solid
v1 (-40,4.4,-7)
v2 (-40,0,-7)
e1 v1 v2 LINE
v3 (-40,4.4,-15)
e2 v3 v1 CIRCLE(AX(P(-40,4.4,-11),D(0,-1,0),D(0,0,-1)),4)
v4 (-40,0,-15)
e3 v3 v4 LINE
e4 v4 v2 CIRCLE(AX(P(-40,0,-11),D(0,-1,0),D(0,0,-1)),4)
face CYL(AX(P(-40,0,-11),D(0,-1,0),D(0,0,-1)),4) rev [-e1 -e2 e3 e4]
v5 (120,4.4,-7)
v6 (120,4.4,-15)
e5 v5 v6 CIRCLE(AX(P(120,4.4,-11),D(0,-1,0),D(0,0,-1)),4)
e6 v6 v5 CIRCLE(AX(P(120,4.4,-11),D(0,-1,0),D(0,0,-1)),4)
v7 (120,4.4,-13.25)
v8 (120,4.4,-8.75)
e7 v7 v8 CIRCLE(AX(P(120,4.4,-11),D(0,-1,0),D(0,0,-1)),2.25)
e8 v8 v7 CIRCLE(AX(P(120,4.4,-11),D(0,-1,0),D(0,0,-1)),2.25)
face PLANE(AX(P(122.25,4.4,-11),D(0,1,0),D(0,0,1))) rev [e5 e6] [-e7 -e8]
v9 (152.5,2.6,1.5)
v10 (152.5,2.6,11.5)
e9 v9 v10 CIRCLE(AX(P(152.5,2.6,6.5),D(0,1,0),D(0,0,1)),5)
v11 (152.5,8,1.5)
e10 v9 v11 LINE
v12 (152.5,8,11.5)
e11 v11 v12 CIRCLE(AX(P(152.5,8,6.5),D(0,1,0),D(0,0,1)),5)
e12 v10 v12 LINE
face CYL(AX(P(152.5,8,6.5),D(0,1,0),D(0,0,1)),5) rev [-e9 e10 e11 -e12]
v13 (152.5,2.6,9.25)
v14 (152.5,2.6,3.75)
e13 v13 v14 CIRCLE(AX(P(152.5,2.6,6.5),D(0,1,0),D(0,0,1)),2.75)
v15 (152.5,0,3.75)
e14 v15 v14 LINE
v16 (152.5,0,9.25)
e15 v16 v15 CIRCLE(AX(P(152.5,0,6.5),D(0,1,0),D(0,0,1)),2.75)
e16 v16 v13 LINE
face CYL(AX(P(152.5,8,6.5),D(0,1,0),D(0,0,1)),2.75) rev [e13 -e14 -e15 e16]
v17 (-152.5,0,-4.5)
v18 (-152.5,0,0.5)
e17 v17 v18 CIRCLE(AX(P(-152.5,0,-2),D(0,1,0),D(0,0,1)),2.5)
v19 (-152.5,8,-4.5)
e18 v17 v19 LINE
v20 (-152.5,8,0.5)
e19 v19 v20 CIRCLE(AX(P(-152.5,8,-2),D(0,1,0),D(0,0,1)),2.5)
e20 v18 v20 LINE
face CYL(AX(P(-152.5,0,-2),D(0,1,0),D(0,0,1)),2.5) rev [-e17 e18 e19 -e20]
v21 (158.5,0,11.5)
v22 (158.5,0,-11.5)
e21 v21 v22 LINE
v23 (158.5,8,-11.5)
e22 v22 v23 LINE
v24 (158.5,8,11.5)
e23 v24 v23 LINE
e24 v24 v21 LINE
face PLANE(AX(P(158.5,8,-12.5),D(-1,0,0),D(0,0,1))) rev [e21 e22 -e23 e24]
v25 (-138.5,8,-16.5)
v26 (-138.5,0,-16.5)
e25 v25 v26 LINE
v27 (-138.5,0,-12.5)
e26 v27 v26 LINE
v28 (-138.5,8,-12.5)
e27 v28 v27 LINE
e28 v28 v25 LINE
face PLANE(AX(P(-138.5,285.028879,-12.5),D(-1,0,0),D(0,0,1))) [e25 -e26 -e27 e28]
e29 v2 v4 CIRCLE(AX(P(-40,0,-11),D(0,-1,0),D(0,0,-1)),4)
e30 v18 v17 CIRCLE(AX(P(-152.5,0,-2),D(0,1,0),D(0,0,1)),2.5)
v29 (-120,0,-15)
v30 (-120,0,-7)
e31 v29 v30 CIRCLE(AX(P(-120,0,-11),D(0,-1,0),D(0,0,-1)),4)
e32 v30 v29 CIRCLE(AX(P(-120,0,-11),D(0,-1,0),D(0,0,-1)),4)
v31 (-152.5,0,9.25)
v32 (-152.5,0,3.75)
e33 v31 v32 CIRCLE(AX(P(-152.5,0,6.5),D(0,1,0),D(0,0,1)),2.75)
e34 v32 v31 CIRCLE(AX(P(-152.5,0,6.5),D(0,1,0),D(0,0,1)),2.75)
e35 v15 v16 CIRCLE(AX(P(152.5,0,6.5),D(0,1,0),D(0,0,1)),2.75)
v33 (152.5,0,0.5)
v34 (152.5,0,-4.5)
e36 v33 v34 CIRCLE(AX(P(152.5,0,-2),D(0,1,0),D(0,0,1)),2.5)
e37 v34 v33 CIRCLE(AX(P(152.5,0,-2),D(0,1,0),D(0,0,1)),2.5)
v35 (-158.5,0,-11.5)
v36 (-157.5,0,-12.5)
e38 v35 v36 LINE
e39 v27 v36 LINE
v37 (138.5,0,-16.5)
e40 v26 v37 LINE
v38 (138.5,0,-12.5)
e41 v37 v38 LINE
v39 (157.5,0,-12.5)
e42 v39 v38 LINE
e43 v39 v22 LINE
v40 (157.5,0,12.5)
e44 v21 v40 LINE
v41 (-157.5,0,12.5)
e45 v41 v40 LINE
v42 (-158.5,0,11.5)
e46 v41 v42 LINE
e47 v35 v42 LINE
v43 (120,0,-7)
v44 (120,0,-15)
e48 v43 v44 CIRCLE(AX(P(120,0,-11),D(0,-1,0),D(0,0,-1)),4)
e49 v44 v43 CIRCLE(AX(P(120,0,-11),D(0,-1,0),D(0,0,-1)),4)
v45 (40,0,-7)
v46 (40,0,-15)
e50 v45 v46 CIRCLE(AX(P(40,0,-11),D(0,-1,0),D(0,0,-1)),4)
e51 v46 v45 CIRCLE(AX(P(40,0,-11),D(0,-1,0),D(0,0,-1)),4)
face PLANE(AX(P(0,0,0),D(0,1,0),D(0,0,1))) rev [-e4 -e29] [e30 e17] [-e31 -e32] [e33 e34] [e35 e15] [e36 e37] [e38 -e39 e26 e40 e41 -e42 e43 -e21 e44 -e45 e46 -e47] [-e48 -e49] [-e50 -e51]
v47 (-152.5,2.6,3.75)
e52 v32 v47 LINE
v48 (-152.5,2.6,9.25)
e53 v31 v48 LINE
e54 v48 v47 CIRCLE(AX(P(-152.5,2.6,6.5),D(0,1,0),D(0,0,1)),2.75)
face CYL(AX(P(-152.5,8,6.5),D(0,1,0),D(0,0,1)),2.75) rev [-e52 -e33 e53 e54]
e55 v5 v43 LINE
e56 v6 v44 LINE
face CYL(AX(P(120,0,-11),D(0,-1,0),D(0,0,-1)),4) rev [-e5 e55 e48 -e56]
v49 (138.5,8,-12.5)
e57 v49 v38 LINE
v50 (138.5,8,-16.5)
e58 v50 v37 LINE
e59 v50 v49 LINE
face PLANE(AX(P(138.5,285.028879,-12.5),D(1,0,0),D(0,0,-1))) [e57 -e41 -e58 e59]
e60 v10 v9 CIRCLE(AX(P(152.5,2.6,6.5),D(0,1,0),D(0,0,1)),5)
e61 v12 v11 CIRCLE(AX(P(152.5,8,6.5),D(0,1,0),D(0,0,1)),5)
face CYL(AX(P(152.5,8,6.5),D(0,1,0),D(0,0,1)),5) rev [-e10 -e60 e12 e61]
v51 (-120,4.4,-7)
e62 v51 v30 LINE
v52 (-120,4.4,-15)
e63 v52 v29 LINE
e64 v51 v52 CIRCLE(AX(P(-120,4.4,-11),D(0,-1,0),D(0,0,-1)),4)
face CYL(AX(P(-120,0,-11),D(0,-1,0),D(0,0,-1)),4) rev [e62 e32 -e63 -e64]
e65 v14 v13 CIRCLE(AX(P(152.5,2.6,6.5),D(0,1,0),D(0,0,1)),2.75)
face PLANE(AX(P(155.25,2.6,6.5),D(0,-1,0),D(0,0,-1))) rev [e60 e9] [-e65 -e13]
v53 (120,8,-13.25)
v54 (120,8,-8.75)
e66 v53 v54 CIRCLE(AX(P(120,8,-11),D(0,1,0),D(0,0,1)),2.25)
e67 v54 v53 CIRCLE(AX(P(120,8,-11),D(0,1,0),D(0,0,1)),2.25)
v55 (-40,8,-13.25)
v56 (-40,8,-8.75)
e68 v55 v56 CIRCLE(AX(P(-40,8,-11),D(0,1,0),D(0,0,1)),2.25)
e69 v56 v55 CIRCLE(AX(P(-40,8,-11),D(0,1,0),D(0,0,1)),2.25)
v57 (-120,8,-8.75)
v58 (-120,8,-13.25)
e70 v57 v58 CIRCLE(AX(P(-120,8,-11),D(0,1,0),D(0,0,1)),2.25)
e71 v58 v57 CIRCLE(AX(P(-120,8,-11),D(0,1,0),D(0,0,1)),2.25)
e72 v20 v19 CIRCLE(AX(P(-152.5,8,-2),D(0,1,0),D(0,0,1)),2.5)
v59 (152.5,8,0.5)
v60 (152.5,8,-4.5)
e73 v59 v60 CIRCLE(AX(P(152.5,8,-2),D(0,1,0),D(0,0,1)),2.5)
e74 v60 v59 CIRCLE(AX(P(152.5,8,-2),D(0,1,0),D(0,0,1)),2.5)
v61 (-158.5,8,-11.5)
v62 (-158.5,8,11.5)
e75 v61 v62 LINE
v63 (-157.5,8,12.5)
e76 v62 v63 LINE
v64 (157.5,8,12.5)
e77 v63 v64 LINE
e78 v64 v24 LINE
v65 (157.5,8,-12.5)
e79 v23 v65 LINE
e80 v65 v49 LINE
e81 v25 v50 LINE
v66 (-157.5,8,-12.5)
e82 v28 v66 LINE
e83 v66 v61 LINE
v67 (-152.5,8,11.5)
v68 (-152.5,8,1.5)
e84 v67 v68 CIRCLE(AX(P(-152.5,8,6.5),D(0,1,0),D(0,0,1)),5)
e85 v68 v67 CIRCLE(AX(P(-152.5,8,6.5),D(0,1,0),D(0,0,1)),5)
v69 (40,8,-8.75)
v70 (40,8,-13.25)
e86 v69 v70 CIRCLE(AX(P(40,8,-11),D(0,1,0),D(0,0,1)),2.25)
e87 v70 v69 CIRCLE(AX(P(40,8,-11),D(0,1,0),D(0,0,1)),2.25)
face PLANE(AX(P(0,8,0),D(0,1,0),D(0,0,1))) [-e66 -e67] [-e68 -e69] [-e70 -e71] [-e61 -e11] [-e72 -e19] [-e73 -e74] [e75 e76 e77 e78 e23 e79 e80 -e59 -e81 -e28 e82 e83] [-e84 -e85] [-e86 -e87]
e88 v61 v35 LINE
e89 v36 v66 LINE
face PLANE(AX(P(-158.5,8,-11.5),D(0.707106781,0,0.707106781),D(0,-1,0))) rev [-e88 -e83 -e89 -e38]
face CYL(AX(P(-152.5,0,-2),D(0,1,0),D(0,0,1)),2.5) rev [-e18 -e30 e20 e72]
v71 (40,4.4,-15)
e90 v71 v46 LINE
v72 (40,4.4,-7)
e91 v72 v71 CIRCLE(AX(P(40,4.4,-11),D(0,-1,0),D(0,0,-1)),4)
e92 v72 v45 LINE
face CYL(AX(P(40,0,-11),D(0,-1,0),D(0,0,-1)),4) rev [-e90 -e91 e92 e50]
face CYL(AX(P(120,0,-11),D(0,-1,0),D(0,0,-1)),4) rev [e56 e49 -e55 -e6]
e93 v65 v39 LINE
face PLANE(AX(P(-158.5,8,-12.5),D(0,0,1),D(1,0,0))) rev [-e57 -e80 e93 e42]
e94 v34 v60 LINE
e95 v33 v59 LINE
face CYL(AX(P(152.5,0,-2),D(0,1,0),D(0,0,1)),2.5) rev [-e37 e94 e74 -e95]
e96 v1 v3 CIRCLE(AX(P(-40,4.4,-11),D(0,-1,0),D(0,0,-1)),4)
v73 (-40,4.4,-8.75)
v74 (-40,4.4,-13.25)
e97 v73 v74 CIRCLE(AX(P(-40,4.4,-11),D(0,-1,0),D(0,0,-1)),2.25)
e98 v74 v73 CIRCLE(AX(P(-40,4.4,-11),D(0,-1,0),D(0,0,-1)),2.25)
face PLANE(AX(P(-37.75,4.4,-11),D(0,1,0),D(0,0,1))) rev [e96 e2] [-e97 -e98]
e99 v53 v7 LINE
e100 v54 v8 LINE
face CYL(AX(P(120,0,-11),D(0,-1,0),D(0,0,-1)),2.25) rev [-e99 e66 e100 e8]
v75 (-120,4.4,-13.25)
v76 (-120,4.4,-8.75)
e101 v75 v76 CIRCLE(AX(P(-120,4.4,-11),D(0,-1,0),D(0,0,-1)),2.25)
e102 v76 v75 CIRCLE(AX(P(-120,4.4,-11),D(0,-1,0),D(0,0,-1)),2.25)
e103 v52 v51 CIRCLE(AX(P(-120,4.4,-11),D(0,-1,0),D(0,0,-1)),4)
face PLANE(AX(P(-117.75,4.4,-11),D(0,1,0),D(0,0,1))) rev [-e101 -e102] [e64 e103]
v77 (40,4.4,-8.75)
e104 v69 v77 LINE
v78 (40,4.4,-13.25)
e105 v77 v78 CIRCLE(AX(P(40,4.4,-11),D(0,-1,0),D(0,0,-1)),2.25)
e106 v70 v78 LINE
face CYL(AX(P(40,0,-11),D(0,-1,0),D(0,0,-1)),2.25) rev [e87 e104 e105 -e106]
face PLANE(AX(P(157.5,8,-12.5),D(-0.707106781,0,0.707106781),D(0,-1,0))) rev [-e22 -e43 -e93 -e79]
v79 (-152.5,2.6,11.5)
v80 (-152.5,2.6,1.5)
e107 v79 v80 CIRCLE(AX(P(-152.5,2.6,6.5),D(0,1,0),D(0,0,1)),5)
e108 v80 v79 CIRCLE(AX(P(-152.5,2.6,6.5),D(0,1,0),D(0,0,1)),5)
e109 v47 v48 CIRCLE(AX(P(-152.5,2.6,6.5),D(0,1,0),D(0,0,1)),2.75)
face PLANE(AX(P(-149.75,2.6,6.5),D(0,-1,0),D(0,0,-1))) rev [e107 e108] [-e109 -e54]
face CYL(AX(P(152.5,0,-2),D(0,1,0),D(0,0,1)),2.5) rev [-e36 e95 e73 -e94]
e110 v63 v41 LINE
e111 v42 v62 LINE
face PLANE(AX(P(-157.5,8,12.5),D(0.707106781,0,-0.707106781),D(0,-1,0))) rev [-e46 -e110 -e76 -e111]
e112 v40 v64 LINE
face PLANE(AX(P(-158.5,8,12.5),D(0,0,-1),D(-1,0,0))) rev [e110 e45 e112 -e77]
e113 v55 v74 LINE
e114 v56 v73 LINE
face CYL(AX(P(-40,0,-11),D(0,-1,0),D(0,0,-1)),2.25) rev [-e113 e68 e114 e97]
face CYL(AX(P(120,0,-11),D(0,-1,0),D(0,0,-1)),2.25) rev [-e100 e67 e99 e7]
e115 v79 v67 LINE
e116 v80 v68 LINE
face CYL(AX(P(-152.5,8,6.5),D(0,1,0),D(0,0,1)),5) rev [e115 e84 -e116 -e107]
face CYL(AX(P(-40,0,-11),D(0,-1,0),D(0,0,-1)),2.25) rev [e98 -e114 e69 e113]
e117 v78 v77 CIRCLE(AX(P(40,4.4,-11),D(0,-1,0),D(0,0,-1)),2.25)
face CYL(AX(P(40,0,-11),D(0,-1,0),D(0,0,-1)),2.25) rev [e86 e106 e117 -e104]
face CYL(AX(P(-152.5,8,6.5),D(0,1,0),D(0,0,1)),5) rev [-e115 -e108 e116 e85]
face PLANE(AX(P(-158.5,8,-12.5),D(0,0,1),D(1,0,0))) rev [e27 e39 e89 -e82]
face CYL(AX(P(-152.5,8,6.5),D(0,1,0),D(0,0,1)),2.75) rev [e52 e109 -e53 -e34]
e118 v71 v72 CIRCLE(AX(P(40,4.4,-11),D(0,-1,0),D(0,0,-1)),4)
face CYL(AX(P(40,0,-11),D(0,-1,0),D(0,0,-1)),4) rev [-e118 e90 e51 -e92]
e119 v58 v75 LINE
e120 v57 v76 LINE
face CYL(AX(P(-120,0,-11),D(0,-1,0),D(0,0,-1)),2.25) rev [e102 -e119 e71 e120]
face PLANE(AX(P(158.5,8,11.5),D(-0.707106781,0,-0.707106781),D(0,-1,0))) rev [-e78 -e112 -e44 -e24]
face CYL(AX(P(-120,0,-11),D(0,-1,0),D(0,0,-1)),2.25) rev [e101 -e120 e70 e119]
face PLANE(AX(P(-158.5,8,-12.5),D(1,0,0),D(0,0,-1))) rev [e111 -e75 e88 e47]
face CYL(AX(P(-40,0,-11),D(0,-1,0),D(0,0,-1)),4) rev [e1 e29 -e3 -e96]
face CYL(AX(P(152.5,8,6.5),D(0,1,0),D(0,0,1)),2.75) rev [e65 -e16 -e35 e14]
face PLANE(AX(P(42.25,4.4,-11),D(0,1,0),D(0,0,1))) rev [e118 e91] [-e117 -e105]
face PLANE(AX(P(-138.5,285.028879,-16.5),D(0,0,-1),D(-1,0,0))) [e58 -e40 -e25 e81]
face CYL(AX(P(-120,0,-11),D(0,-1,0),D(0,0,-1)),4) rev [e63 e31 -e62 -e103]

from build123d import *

# Parameters (mm, degrees)
SKETCH_1_W                   = 317
SKETCH_1_H                   = 25
EXTRUDE_1_DEPTH              = 8
HOLE_WIZARD_M5_1_D           = 5.5
HOLE_WIZARD_M5_1_CBORE_D     = 10
HOLE_WIZARD_M5_1_CBORE_DEPTH = 5.4
SKETCH_4_R                   = 2.5
CUT_EXTRUDE_1_DEPTH          = 160.193278753
SKETCH_7_W                   = 277
SKETCH_7_H                   = 4
EXTRUDE_2_DEPTH              = 8
HOLE_WIZARD_M4_1_D           = 4.5
HOLE_WIZARD_M4_1_CBORE_D     = 8
HOLE_WIZARD_M4_1_CBORE_DEPTH = 4.4
CHAMFER_3_SIZE               = 1


with BuildPart() as part:
    # 草图1 → 凸台-拉伸1 (new body)
    with BuildSketch(Plane(origin=(0, 0, 0), x_dir=(1, 0, 0), z_dir=(0, 1, 0))):
        Rectangle(SKETCH_1_W, SKETCH_1_H)
    extrude(amount=EXTRUDE_1_DEPTH)

    # M5 六角凹头螺钉的柱形沉头孔1 (through all)
    with Locations(Plane(origin=(0, 8, 0), x_dir=(1, 0, 0), z_dir=(0, 1, 0))):
        with Locations((-152.5, -6.5), (152.5, -6.5)):
            CounterBoreHole(HOLE_WIZARD_M5_1_D / 2, HOLE_WIZARD_M5_1_CBORE_D / 2, HOLE_WIZARD_M5_1_CBORE_DEPTH)

    # 草图4 → 切除-拉伸1 (cut, through all)
    with BuildSketch(Plane(origin=(0, 8, 0), x_dir=(1, 0, 0), z_dir=(0, 1, 0))):
        with Locations(Location((-152.5, 2, 0), (0, 0, 270))):
            Circle(SKETCH_4_R)
        with Locations(Location((152.5, 2, 0), (0, 0, 270))):
            Circle(SKETCH_4_R)
    extrude(amount=-CUT_EXTRUDE_1_DEPTH, mode=Mode.SUBTRACT)

    # 草图7 → 凸台-拉伸2 (add)
    with BuildSketch(Plane.XZ):
        with Locations((0, -14.5)):
            Rectangle(SKETCH_7_W, SKETCH_7_H)
    extrude(amount=-EXTRUDE_2_DEPTH)

    # M4 六角凹头螺钉的柱形沉头孔1 (through all)
    with Locations(Plane(origin=(0, 0, 0), x_dir=(-1, 0, 0), z_dir=(0, -1, 0))):
        with Locations((-120, 11), (-40, 11), (40, 11), (120, 11)):
            CounterBoreHole(HOLE_WIZARD_M4_1_D / 2, HOLE_WIZARD_M4_1_CBORE_D / 2, HOLE_WIZARD_M4_1_CBORE_DEPTH)

    # 倒角3
    chamfer_3_edges = [part.edges().sort_by_distance(p)[0] for p in [
        (-158.5, 4, -12.5),
        (-158.5, 4, 12.5),
        (158.5, 4, -12.5),
        (158.5, 4, 12.5),
    ]]
    chamfer(chamfer_3_edges, length=CHAMFER_3_SIZE)


solid = part.part
